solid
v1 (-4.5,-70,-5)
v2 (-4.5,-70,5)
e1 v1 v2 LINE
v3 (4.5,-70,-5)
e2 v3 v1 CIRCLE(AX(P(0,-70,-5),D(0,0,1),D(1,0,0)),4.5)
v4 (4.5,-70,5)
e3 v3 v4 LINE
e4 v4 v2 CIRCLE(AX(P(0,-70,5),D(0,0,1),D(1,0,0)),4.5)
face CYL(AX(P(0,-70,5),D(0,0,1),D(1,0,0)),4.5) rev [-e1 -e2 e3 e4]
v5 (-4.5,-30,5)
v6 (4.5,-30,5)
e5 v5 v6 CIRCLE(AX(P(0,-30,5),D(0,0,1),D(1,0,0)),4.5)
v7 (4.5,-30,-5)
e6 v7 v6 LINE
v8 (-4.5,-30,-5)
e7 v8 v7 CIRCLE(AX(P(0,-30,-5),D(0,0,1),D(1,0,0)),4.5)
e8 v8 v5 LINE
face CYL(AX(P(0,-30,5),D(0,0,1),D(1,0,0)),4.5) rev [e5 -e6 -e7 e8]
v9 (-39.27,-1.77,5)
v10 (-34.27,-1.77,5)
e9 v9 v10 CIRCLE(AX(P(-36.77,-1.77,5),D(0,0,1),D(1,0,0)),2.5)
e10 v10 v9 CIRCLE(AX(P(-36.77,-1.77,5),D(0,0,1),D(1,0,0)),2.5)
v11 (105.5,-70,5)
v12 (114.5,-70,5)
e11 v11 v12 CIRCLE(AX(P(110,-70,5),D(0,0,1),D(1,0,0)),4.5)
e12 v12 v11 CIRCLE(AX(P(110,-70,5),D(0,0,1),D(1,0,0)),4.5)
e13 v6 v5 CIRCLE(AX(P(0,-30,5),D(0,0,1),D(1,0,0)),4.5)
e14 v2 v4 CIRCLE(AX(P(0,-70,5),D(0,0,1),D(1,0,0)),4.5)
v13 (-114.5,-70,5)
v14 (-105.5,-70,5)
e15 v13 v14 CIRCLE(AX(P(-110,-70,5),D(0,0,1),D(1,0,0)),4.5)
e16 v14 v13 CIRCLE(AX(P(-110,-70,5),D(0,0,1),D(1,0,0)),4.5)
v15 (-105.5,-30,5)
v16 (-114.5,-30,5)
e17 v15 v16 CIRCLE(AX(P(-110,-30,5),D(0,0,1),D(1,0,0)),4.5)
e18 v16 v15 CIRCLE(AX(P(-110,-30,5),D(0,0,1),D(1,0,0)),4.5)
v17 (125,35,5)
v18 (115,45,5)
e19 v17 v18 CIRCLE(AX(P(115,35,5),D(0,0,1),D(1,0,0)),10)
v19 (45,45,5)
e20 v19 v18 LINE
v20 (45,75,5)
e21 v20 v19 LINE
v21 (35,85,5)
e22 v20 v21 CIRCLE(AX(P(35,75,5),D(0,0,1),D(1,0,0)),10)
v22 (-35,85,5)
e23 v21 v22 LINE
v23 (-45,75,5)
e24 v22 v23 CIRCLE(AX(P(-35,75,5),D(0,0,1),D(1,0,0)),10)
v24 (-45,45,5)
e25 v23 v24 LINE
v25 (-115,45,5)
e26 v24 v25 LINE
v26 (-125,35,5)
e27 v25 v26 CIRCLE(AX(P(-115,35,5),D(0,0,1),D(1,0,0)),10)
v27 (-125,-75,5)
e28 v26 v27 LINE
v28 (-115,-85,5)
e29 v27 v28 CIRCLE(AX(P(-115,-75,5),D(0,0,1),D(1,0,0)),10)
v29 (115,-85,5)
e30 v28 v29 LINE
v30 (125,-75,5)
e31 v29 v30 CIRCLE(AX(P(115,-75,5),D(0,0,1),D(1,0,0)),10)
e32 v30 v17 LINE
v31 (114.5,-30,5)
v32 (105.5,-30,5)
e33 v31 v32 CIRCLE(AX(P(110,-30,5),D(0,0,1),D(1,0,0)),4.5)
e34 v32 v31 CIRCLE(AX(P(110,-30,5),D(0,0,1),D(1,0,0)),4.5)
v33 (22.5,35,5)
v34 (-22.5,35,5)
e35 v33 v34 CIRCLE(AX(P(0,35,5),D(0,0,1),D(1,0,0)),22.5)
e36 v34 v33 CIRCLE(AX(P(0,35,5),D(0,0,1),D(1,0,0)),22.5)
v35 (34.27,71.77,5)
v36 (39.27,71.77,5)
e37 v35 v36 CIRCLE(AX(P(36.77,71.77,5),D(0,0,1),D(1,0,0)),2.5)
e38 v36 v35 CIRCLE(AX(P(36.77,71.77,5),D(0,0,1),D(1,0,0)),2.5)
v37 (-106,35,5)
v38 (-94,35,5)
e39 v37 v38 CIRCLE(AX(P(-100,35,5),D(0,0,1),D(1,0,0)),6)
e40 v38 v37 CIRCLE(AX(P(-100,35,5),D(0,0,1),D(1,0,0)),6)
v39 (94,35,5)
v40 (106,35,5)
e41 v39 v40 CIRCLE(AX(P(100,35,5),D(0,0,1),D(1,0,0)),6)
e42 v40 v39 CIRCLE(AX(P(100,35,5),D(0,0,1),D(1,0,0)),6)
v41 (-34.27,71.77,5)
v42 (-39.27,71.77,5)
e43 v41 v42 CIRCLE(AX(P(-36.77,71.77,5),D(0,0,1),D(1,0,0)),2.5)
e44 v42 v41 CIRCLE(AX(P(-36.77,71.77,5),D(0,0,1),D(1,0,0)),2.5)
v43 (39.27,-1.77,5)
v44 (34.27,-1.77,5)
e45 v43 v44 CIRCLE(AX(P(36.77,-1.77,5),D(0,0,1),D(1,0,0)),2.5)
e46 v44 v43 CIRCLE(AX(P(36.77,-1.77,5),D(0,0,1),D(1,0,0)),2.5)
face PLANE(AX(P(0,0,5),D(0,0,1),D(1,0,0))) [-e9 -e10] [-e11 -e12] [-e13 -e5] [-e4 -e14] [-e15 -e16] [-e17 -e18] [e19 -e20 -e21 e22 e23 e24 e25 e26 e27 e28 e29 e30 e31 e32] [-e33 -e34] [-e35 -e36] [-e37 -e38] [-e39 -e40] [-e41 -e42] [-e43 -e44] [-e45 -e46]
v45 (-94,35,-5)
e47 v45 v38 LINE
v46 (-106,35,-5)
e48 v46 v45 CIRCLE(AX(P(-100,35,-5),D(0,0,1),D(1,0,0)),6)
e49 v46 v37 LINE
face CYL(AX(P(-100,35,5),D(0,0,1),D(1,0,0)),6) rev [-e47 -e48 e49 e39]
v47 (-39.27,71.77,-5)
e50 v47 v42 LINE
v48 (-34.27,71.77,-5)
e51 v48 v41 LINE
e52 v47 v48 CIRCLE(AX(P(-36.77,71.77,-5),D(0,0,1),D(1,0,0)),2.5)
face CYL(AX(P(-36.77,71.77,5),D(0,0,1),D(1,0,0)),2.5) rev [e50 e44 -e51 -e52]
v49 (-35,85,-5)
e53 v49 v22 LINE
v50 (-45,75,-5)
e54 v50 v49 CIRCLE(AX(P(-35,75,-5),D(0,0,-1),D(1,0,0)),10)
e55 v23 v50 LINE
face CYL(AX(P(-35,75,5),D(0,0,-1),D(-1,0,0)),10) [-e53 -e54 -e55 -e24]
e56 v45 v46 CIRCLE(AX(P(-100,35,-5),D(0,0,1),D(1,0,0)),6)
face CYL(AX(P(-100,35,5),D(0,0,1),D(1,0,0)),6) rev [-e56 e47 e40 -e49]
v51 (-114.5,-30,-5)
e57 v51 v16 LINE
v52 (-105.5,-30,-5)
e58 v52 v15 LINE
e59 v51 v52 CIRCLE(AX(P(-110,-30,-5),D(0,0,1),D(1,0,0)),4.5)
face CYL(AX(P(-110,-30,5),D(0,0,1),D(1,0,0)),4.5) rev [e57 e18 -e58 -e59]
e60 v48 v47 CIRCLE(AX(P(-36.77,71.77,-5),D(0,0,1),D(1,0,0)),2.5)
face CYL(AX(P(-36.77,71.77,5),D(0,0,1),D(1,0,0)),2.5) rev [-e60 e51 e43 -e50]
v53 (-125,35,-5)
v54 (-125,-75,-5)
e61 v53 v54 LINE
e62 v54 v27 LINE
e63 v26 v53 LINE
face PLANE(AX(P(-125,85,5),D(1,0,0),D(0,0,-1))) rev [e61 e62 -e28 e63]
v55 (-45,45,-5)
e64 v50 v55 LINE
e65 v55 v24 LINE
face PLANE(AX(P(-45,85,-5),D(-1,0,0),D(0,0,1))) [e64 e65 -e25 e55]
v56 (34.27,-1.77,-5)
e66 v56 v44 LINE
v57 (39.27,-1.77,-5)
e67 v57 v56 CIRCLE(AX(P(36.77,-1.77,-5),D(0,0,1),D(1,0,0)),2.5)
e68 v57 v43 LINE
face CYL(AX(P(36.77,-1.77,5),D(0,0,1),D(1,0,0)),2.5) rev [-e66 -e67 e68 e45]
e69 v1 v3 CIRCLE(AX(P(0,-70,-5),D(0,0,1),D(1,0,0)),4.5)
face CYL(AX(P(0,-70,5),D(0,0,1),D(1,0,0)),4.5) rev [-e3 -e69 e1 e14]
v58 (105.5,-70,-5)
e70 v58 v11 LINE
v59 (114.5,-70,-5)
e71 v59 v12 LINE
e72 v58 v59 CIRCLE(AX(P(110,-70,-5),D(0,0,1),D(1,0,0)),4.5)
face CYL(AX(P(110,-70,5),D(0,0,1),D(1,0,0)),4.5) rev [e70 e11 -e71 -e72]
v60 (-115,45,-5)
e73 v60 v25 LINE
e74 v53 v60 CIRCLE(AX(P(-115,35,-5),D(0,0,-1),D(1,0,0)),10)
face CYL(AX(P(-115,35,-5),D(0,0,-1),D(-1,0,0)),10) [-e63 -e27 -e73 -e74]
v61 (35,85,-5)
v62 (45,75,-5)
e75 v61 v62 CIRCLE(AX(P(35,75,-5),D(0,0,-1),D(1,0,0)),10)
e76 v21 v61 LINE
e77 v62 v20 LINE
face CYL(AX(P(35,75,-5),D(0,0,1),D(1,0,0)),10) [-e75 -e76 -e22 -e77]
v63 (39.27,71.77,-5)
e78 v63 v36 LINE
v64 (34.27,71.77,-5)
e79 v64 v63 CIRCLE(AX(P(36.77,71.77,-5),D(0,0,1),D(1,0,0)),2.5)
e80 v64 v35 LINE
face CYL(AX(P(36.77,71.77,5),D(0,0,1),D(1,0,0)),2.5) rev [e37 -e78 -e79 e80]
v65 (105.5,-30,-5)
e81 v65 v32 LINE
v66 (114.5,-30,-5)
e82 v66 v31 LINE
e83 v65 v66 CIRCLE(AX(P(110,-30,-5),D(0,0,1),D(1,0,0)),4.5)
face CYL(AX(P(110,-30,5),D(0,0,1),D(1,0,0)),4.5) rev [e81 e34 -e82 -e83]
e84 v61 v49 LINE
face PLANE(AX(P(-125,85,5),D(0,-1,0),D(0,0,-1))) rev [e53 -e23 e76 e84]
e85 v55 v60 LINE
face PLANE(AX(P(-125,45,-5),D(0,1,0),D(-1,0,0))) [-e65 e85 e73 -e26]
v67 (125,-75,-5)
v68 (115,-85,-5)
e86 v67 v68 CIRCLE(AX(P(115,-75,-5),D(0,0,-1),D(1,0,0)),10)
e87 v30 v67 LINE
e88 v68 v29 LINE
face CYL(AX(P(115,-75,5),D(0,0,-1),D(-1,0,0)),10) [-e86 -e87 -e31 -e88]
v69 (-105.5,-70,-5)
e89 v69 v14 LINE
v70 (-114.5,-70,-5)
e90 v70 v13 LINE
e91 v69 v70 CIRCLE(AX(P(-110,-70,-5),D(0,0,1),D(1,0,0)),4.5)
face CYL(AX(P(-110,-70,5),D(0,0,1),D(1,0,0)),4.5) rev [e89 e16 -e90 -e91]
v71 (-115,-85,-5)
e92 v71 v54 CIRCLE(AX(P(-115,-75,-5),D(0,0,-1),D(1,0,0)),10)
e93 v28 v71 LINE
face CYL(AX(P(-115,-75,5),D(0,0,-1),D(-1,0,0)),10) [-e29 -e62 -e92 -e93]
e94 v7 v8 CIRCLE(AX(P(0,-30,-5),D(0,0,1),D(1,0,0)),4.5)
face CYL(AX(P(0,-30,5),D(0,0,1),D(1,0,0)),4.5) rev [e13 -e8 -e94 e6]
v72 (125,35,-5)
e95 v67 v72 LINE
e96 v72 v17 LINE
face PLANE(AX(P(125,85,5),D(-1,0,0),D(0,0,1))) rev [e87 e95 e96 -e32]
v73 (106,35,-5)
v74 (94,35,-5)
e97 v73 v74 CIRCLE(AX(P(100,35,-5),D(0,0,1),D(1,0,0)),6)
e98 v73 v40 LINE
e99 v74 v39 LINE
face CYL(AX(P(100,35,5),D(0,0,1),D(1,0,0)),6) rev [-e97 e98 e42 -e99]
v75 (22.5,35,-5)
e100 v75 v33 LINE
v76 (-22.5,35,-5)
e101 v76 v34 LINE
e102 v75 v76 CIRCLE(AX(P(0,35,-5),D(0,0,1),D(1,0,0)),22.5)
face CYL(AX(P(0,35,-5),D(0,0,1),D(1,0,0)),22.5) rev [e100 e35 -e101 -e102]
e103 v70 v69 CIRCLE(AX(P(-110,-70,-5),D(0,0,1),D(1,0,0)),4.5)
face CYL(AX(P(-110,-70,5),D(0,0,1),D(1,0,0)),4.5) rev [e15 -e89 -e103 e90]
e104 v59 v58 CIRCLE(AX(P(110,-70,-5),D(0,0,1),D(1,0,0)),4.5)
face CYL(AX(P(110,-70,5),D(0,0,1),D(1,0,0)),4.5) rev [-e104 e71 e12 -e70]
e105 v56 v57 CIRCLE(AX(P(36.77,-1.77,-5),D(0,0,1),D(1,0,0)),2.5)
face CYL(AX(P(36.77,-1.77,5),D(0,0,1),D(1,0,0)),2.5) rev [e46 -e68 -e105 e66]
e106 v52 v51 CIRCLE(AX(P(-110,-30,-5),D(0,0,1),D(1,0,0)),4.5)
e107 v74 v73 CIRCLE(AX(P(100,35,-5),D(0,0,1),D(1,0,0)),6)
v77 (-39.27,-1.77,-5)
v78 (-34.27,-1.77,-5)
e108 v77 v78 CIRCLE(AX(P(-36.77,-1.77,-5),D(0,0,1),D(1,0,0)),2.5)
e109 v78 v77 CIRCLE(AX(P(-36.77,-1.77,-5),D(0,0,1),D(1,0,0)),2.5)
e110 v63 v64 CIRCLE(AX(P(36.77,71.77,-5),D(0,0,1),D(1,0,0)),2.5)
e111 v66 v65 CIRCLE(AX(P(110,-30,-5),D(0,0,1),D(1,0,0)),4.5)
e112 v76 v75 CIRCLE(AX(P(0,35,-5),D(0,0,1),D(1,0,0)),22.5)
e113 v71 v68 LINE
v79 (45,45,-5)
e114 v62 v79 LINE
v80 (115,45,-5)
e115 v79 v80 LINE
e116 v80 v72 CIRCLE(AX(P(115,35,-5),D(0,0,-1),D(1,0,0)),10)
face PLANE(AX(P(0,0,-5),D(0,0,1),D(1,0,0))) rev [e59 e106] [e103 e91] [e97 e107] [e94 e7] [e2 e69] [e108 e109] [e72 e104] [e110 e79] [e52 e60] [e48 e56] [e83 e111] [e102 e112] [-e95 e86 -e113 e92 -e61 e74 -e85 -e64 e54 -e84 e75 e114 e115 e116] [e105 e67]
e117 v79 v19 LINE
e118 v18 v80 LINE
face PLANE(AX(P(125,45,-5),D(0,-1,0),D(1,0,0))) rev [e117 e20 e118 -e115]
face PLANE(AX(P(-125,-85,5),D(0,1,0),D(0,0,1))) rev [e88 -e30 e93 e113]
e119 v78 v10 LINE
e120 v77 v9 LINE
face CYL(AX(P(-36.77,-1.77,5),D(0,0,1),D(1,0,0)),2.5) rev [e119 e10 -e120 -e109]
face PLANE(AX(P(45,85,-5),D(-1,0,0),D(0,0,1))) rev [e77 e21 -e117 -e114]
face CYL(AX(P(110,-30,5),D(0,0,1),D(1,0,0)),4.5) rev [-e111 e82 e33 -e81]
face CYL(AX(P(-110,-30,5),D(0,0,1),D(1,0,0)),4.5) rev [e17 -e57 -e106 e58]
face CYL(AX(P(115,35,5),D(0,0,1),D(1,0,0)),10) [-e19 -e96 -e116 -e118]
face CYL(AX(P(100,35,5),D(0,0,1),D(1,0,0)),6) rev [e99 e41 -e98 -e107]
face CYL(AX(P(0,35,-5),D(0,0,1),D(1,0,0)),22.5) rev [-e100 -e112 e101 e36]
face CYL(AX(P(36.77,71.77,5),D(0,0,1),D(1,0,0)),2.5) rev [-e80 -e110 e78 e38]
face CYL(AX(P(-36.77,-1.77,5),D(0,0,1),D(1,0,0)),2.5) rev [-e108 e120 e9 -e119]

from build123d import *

# Parameters (mm, degrees)
SKETCH_1_W                = 250
SKETCH_1_H                = 170
EXTRUDE_1_DEPTH           = 5
SKETCH_2_W                = 80
SKETCH_2_H                = 40
CUT_EXTRUDE_1_DEPTH       = 10
HOLE_WIZARD_9_0_9_1_D     = 9
PATTERN_LINEAR_1_COUNT    = 3
PATTERN_LINEAR_1_PITCH    = 110
HOLE_WIZARD_12_0_12_1_D   = 12
SKETCH_7_R                = 22.5
CUT_EXTRUDE_2_DEPTH       = 10
HOLE_WIZARD_M6_1_D        = 5
PATTERN_LINEAR_3_COUNT    = 2
PATTERN_LINEAR_3_PITCH    = 73.54
PATTERN_LINEAR_4_COUNT    = 2
PATTERN_LINEAR_4_PITCH    = 73.54
PATTERN_LINEAR_4_COPY_1_D = 5
FILLET_1_R                = 10


with BuildPart() as part:
    # 草图1 → 凸台-拉伸1 (new, symmetric)
    with BuildSketch(Plane.XY):
        Rectangle(SKETCH_1_W, SKETCH_1_H)
    extrude(amount=EXTRUDE_1_DEPTH, both=True)

    # 草图2 → 切除-拉伸1 (cut)
    with BuildSketch(Plane.XY.offset(5)):
        with Locations((85, 65)):
            Rectangle(SKETCH_2_W, SKETCH_2_H)
    cut_extrude_1 = extrude(amount=-CUT_EXTRUDE_1_DEPTH, mode=Mode.SUBTRACT)

    # 镜向1: 切除-拉伸1 across plane
    add(cut_extrude_1.mirror(Plane(origin=(0, 0, 0), x_dir=(0, 0, 1), z_dir=(1, 0, 0))), mode=Mode.SUBTRACT)

    # Ø9.0 (9) 直径孔1 (through all)
    with Locations(Plane.XY.offset(5)):
        with Locations((-110, -70), (-110, -30)):
            hole_wizard_9_0_9_1 = Hole(HOLE_WIZARD_9_0_9_1_D / 2)

    # 阵列(线性)1: Ø9.0 (9) 直径孔1 ×3
    with Locations(*[(i * PATTERN_LINEAR_1_PITCH, 0, 0) for i in range(1, PATTERN_LINEAR_1_COUNT)]):
        add(hole_wizard_9_0_9_1, mode=Mode.SUBTRACT)

    # Ø12.0 (12) 直径孔1 (through all)
    with Locations(Plane.XY.offset(5)):
        with Locations((-100, 35), (100, 35)):
            Hole(HOLE_WIZARD_12_0_12_1_D / 2)

    # 草图7 → 切除-拉伸2 (cut)
    with BuildSketch(Plane.XY.offset(5)):
        with Locations((0, 35)):
            Circle(SKETCH_7_R)
    extrude(amount=-CUT_EXTRUDE_2_DEPTH, mode=Mode.SUBTRACT)

    # M6 螺纹孔1 (through all)
    with Locations(Plane.XY.offset(5)):
        with Locations((-36.77, 71.77)):
            hole_wizard_m6_1 = Hole(HOLE_WIZARD_M6_1_D / 2)

    # 阵列(线性)3: M6 螺纹孔1 ×2
    with Locations(*[(0, -i * PATTERN_LINEAR_3_PITCH, 0) for i in range(1, PATTERN_LINEAR_3_COUNT)]):
        add(hole_wizard_m6_1, mode=Mode.SUBTRACT)

    # 阵列(线性)4: M6 螺纹孔1 ×2
    with Locations(*[(i * PATTERN_LINEAR_4_PITCH, 0, 0) for i in range(1, PATTERN_LINEAR_4_COUNT)]):
        add(hole_wizard_m6_1, mode=Mode.SUBTRACT)

    # 阵列(线性)4 copy 1 (through all)
    with Locations(Plane(origin=(73.54, -73.54, 5), x_dir=(1, 0, 0), z_dir=(0, 0, 1))):
        with Locations((-36.77, 71.77)):
            Hole(PATTERN_LINEAR_4_COPY_1_D / 2)

    # 圆角1
    fillet_1_edges = [part.edges().sort_by_distance(p)[0] for p in [
        (125, 45, 0),
        (45, 85, 0),
        (-125, 45, 0),
        (-45, 85, 0),
        (125, -85, 0),
        (-125, -85, 0),
    ]]
    fillet(fillet_1_edges, radius=FILLET_1_R)


solid = part.part
